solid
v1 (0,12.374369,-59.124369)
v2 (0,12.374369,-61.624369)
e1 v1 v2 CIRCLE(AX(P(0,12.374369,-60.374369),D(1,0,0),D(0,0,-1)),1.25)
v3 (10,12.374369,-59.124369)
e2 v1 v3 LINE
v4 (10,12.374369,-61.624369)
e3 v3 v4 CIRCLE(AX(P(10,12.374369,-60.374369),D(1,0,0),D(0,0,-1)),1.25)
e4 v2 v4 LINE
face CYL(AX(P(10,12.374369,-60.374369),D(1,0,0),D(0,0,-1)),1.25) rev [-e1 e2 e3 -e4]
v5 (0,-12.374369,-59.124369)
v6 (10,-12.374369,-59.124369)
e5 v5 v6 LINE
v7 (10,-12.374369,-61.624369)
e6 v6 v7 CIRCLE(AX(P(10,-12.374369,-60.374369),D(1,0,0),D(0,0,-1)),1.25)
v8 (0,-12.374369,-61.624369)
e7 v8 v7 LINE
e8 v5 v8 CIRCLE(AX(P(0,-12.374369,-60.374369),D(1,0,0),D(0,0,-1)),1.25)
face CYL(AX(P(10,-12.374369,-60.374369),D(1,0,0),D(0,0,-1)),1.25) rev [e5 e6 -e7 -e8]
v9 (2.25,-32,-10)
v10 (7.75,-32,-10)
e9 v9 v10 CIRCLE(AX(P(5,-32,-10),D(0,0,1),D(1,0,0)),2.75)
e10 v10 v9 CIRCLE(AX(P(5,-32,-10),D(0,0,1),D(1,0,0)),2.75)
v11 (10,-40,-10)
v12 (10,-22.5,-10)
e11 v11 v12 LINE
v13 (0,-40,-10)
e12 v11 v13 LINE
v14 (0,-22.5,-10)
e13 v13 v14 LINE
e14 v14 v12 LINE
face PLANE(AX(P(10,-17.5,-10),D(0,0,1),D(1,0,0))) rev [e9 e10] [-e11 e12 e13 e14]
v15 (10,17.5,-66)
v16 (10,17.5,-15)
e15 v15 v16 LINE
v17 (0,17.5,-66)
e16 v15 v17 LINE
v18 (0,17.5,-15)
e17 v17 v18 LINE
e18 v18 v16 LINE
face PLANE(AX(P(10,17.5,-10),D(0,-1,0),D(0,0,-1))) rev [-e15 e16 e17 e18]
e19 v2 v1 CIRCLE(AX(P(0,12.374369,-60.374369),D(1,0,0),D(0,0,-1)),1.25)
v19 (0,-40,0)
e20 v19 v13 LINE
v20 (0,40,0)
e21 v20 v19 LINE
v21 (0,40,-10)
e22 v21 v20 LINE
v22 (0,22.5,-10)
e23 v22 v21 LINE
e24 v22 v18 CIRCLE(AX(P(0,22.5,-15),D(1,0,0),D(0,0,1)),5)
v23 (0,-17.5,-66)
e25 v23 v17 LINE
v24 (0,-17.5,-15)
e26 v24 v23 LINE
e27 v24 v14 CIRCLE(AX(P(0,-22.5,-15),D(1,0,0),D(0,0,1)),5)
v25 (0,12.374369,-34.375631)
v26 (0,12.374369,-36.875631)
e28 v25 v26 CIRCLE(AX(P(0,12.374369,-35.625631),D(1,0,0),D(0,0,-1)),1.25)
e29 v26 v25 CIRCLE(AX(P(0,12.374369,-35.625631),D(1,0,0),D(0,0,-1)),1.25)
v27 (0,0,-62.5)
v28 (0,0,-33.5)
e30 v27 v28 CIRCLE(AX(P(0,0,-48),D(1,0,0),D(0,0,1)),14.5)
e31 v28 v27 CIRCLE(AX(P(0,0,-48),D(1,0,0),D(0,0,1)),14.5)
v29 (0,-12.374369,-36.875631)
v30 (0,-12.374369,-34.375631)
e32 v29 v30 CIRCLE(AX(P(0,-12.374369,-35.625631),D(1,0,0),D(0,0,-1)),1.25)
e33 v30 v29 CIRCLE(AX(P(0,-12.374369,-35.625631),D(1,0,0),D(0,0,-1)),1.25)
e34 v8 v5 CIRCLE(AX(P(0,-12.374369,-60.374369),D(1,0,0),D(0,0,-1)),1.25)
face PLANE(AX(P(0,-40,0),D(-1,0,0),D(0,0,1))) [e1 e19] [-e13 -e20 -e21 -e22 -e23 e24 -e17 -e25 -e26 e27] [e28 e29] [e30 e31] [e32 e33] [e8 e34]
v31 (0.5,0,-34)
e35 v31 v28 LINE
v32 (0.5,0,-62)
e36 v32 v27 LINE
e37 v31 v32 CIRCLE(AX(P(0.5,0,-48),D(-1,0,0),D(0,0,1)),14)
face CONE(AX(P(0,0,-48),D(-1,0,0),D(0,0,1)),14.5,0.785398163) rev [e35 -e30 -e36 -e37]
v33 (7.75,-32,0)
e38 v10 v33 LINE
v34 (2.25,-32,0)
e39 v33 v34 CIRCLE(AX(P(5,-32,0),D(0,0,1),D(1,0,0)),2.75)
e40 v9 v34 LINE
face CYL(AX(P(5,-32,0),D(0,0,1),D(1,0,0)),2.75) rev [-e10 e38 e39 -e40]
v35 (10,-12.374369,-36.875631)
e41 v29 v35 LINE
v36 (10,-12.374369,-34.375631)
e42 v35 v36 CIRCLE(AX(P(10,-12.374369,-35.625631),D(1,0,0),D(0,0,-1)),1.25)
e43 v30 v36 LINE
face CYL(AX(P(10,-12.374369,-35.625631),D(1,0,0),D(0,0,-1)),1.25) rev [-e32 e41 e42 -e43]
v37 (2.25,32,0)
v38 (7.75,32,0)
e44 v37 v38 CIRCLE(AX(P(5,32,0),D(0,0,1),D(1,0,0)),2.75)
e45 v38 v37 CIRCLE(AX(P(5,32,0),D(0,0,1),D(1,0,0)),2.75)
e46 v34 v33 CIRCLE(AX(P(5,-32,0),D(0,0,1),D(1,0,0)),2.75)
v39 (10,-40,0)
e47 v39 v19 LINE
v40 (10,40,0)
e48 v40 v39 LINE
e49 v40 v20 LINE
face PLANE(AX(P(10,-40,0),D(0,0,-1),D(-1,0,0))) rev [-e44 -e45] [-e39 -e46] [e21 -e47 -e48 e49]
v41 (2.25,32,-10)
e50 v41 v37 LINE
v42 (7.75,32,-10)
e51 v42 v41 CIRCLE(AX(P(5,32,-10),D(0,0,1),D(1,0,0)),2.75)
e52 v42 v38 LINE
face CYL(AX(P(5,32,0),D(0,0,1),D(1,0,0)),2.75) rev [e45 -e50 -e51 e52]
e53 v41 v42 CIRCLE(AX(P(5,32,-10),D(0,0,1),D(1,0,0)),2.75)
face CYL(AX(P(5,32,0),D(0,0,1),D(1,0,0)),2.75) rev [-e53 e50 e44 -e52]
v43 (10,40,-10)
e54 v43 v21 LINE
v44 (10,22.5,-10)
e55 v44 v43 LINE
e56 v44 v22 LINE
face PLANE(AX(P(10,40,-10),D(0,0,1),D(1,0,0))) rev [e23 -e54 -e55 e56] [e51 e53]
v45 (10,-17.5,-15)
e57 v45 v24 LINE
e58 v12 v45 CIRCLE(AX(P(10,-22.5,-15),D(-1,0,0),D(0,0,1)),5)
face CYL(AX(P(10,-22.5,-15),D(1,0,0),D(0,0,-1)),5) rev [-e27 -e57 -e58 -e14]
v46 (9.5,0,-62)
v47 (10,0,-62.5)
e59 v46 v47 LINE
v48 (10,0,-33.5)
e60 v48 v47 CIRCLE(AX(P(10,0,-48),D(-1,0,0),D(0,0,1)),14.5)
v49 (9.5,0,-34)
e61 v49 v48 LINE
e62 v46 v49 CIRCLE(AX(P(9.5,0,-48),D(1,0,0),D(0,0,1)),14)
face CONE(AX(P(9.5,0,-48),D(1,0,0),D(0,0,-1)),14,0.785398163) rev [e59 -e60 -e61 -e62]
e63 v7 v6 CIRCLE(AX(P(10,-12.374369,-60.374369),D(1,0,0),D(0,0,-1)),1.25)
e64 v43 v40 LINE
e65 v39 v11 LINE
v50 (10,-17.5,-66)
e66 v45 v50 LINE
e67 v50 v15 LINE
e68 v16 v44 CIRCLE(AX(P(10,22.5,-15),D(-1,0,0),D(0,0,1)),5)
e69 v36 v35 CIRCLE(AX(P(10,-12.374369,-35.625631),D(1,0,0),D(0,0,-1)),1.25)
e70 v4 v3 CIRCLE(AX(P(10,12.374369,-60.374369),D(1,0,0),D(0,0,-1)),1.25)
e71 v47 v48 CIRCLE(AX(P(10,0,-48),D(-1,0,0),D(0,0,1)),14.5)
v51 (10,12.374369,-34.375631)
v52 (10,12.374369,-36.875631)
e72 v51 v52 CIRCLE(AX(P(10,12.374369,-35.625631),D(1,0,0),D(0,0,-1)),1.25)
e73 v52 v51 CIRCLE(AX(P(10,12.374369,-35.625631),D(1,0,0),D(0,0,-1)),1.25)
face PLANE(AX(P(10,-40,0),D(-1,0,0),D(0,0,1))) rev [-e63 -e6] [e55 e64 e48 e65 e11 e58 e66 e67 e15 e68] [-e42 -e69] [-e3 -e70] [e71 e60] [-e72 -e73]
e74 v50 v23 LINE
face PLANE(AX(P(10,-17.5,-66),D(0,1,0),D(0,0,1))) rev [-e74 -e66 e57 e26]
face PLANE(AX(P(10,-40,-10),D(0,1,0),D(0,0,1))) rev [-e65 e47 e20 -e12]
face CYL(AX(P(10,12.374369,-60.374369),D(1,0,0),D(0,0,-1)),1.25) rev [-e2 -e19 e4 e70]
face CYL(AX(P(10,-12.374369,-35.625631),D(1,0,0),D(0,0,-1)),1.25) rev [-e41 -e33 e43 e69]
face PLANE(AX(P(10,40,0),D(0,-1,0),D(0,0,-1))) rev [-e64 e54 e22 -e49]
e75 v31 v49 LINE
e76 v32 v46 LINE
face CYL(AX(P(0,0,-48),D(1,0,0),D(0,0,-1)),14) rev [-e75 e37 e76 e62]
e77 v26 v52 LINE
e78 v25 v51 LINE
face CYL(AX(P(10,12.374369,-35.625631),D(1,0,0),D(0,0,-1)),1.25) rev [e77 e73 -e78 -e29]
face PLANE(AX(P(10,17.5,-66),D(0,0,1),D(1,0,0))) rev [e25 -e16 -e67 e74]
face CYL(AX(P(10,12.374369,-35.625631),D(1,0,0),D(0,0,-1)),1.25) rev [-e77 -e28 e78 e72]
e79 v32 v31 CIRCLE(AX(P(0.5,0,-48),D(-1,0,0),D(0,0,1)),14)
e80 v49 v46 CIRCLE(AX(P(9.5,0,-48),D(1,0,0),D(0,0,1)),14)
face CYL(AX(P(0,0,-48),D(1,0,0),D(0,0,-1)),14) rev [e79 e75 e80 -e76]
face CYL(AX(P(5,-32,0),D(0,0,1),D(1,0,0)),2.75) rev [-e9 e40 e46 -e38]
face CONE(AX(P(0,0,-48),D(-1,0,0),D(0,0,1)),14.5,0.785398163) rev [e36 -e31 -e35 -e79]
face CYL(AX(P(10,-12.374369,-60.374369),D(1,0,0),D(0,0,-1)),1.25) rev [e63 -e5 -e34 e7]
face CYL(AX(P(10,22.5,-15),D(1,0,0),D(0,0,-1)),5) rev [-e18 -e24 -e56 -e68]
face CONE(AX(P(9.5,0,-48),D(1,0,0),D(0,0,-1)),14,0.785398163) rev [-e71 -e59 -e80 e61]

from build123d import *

# Parameters (mm, degrees)
BOSS_EXTRUDE1_DEPTH        = 10
SKETCH2_R                  = 14
CUT_EXTRUDE1_DEPTH         = 78.820305833
F_5_5_5_5_DIAMETER_HOLE1_D = 5.5
M3_TAPPED_HOLE1_D          = 2.5
FILLET1_R                  = 5
CHAMFER1_SIZE              = 0.5


with BuildPart() as part:
    # Sketch1 → Boss-Extrude1 (new body)
    with BuildSketch(Plane(origin=(0, 0, 0), x_dir=(0, 0, -1), z_dir=(1, 0, 0))):
        Polygon((0, -40), (0, 40), (10, 40), (10, 17.5), (66, 17.5), (66, -17.5), (10, -17.5), (10, -40), align=None)
    extrude(amount=BOSS_EXTRUDE1_DEPTH)

    # Sketch2 → Cut-Extrude1 (cut, through all)
    with BuildSketch(Plane(origin=(10, 0, 0), x_dir=(0, 0, -1), z_dir=(1, 0, 0))):
        with Locations((48, 0)):
            Circle(SKETCH2_R)
    extrude(amount=-CUT_EXTRUDE1_DEPTH, mode=Mode.SUBTRACT)

    # Ø5.5 (5.5) Diameter Hole1 (through all)
    with Locations(Plane.XY):
        with Locations((5, 32), (5, -32)):
            Hole(F_5_5_5_5_DIAMETER_HOLE1_D / 2)

    # M3 Tapped Hole1 (through all)
    with Locations(Plane(origin=(10, 0, 0), x_dir=(0, 0, -1), z_dir=(1, 0, 0))):
        with Locations((35.625631329, 12.374368671), (60.374368671, 12.374368671), (60.374368671, -12.374368671), (35.625631329, -12.374368671)):
            Hole(M3_TAPPED_HOLE1_D / 2)

    # Fillet1
    fillet1_edges = [part.edges().sort_by_distance(p)[0] for p in [
        (5, 17.5, -10),
        (5, -17.5, -10),
    ]]
    fillet(fillet1_edges, radius=FILLET1_R)

    # Chamfer1
    chamfer1_edges = [part.edges().sort_by_distance(p)[0] for p in [
        (0, 0, -34),
        (10, 0, -34),
    ]]
    chamfer(chamfer1_edges, length=CHAMFER1_SIZE)


solid = part.part
